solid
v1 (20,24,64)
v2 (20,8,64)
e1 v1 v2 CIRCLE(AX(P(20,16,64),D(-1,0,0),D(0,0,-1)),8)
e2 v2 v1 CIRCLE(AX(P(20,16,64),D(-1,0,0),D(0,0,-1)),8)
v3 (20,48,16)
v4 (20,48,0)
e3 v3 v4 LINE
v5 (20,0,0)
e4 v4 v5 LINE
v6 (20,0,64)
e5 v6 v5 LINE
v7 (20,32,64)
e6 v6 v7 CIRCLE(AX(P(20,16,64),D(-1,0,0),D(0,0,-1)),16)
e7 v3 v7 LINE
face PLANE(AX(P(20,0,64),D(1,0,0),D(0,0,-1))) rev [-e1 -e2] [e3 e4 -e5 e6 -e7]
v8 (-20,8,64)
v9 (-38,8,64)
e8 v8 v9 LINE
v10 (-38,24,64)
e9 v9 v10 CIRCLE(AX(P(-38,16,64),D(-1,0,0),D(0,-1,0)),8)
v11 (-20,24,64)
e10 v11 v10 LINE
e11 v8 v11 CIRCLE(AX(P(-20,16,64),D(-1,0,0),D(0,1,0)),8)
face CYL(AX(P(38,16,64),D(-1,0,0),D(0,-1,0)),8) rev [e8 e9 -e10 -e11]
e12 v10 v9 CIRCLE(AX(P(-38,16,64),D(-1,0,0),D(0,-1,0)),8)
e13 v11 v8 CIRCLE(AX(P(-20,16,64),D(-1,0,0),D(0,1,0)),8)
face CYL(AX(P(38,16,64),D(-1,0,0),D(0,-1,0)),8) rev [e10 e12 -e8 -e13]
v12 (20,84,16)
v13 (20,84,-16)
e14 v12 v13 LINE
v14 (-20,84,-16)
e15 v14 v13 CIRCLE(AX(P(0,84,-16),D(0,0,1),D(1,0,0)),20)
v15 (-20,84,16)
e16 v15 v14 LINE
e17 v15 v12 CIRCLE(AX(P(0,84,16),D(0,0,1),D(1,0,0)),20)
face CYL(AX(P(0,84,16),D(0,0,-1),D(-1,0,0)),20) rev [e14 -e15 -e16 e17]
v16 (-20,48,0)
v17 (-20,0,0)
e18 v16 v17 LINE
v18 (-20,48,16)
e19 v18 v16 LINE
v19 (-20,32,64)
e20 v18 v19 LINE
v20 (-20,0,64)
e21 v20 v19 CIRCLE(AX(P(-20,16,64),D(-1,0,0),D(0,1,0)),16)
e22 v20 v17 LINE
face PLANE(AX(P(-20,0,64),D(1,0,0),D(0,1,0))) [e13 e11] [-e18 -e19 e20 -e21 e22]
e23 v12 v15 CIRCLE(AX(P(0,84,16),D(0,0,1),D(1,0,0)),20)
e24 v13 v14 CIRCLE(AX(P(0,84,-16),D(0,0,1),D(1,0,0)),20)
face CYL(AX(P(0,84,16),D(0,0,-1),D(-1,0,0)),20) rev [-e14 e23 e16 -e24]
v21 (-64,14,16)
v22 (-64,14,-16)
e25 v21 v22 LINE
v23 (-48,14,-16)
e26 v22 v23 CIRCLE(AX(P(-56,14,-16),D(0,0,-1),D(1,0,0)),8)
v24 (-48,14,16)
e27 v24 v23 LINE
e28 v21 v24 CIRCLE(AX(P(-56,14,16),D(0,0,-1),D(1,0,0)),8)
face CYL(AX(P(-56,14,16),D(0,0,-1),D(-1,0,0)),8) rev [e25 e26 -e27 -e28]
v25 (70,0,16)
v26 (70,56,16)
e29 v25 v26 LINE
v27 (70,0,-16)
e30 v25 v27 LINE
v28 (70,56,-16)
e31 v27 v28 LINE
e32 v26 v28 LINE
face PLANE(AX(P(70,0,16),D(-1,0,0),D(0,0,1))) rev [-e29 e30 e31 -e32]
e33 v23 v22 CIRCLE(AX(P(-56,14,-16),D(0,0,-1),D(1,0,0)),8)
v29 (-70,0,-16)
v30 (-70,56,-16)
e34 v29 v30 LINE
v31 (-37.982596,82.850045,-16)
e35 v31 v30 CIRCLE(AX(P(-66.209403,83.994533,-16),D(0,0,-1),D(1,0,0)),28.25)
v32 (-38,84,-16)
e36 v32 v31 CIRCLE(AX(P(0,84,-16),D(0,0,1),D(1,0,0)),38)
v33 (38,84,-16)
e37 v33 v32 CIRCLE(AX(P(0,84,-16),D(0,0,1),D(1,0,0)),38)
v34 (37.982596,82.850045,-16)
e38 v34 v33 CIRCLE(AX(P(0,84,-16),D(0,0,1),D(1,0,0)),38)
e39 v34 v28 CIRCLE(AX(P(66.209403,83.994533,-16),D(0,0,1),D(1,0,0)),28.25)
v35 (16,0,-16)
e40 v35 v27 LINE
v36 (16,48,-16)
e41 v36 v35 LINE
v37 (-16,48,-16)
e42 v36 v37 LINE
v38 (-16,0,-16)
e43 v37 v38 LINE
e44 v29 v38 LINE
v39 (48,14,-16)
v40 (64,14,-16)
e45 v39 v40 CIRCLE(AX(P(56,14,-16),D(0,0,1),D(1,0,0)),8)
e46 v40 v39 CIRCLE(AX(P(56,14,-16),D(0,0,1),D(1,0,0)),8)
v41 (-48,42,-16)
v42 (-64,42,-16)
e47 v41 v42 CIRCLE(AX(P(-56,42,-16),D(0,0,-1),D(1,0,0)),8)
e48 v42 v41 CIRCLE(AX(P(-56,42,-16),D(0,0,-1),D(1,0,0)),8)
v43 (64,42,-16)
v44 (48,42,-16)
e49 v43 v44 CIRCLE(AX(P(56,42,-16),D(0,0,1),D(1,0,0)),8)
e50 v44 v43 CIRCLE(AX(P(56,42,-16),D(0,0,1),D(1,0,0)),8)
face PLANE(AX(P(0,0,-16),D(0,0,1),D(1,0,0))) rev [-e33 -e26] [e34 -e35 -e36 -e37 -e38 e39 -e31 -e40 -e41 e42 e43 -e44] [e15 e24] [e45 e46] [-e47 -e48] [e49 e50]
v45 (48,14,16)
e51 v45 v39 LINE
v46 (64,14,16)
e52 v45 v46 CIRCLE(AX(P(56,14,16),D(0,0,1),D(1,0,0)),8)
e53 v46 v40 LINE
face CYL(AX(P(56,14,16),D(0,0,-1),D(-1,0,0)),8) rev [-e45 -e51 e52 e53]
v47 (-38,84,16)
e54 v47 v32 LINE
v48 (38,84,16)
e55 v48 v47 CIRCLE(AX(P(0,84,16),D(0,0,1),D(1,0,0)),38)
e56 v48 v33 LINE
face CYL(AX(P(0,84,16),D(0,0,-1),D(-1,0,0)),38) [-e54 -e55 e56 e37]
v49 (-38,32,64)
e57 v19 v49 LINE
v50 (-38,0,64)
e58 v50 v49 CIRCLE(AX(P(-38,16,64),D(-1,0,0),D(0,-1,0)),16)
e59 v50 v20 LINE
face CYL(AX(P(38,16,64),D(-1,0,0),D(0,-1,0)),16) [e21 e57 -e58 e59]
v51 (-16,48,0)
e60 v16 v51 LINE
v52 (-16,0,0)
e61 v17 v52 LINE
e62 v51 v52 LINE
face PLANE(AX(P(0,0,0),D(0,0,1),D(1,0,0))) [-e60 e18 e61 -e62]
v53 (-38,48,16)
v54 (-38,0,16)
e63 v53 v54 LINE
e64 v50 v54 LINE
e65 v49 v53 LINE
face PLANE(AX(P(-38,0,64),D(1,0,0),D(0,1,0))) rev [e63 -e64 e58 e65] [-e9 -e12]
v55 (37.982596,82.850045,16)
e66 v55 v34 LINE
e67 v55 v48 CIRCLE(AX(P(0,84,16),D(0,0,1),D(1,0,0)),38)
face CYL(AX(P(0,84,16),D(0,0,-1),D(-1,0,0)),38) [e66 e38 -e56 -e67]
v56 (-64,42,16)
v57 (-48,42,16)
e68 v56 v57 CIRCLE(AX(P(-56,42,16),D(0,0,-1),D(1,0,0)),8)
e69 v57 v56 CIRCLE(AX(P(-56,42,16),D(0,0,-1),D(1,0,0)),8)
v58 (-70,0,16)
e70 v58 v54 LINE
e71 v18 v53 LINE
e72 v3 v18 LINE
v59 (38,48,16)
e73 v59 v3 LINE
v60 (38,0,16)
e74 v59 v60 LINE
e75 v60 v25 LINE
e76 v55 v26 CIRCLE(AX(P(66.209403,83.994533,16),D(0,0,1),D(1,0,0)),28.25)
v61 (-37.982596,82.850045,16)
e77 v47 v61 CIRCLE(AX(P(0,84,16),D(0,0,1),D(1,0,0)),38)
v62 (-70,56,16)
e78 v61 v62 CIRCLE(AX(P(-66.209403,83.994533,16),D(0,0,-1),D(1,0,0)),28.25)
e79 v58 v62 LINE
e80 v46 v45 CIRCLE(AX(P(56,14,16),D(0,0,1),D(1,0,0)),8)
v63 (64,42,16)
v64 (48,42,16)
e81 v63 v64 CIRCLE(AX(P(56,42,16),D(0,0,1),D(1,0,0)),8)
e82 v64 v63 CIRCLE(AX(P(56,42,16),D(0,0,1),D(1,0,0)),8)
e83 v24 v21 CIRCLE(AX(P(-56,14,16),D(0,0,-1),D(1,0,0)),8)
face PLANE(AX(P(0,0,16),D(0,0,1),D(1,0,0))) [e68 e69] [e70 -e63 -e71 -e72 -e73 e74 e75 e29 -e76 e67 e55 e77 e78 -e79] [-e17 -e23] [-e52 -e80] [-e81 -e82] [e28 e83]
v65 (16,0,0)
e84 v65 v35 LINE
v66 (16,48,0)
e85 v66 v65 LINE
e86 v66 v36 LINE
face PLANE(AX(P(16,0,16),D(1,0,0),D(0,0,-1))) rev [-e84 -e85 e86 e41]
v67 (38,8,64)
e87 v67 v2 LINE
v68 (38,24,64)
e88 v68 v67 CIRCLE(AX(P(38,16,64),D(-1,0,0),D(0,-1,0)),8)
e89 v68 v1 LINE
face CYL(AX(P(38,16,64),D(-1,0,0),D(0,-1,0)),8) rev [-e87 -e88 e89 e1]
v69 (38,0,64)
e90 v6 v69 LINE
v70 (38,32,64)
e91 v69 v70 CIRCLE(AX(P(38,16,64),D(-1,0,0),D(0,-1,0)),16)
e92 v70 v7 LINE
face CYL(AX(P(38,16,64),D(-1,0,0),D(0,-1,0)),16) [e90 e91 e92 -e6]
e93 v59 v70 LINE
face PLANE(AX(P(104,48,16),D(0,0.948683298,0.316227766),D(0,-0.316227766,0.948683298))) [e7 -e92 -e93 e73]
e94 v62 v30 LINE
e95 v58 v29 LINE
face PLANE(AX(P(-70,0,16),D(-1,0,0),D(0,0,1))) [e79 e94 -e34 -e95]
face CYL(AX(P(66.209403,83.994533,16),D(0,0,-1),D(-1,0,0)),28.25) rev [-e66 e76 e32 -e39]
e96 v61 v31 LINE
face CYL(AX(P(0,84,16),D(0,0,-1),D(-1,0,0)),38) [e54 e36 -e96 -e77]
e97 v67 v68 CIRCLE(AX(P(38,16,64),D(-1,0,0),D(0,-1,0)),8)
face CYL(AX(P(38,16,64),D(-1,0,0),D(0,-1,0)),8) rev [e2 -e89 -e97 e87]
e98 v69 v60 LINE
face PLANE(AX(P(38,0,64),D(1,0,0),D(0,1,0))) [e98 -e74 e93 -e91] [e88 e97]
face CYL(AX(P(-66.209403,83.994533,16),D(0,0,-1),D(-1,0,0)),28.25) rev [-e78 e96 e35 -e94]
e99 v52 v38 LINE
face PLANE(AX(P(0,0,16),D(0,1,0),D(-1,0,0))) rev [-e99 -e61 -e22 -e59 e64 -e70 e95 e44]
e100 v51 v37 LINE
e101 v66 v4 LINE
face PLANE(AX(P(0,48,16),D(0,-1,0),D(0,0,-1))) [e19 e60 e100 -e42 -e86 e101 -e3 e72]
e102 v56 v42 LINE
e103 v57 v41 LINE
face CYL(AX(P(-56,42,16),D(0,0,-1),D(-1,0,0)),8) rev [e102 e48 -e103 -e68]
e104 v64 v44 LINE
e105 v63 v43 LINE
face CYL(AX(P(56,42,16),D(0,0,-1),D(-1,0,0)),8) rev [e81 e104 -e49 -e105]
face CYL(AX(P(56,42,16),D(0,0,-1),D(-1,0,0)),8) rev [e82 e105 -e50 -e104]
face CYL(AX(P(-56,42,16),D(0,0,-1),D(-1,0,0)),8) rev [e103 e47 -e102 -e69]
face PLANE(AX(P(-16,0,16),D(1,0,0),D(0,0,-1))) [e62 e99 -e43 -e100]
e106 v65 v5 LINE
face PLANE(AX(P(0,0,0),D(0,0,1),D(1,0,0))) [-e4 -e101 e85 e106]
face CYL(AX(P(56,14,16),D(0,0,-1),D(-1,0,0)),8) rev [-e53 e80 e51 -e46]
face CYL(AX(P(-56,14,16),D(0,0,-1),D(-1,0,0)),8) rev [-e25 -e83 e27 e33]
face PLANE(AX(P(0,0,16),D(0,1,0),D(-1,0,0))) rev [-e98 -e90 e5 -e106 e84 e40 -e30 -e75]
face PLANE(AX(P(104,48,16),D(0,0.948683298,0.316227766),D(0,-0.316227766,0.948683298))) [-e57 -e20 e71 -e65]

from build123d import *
from build123d.topology import SkipClean

# Parameters (mm, degrees)
BRACKET_MASTER_PROFILE_SKETCH_R   = 8
BRACKET_MASTER_PROFILE_SKETCH_R_2 = 20
BASE_BLOCK_32MM_DEPTH             = 16
SKETCH1_5_W                       = 18
SKETCH1_5_H                       = 48
BORE_BOSS_BODY_64MM_DEPTH         = 64
CLEVIS_LUGS_76MM_DEPTH            = 76
LUG_PROFILE_CUT_A_DEPTH           = 142
LUG_PROFILE_CUT_B_DEPTH           = 142
SKETCH1_6_W                       = 32
SKETCH1_6_H                       = 48
PROFILE_CUT_131MM_DEPTH           = 131
SKETCH1_7_W                       = 18
SKETCH1_7_H                       = 48
PROFILE_BOSS_16MM_DEPTH           = 16
SKETCH1_15_W                      = 4
SKETCH1_15_H                      = 48
PROFILE_BOSS_32MM_DEPTH           = 16
SKETCH1_16_W                      = 4
SKETCH1_16_H                      = 48
THROUGH_CUT_147MM_DEPTH           = 147


with BuildPart() as part:
    # Bracket Master Profile Sketch → Base Block 32mm (new, symmetric)
    with BuildSketch(Plane.XY):
        with BuildLine():
            Line((-70, 56), (-70, 0))
            Line((-70, 0), (-38, 0))
            Line((-38, 0), (-38, 48))
            Line((-38, 48), (-20, 48))
            Line((-20, 48), (-16, 48))
            Line((-16, 48), (16, 48))
            Line((16, 48), (20, 48))
            Line((20, 48), (38, 48))
            Line((38, 48), (38, 0))
            Line((38, 0), (70, 0))
            Line((70, 0), (70, 56))
            ThreePointArc((70, 56), (48.056901395, 62.34853625), (37.98259606, 82.850044997))
            ThreePointArc((37.98259606, 82.850044997), (0, 122), (-37.98259606, 82.850044997))
            ThreePointArc((-37.98259606, 82.850044997), (-48.056901395, 62.34853625), (-70, 56))
        make_face()
        with Locations((-56, 14)):
            Circle(BRACKET_MASTER_PROFILE_SKETCH_R, mode=Mode.SUBTRACT)
        with Locations((-56, 42)):
            Circle(BRACKET_MASTER_PROFILE_SKETCH_R, mode=Mode.SUBTRACT)
        with Locations((56, 14)):
            Circle(BRACKET_MASTER_PROFILE_SKETCH_R, mode=Mode.SUBTRACT)
        with Locations((56, 42)):
            Circle(BRACKET_MASTER_PROFILE_SKETCH_R, mode=Mode.SUBTRACT)
        with Locations((0, 84)):
            Circle(BRACKET_MASTER_PROFILE_SKETCH_R_2, mode=Mode.SUBTRACT)
    extrude(amount=BASE_BLOCK_32MM_DEPTH, both=True)

    # Sketch1_5 → Bore Boss Body 64mm (add)
    with BuildSketch(Plane.XY):
        with Locations((-29, 24)):
            Rectangle(SKETCH1_5_W, SKETCH1_5_H)
        with Locations((29, 24)):
            Rectangle(SKETCH1_5_W, SKETCH1_5_H)
    extrude(amount=BORE_BOSS_BODY_64MM_DEPTH)

    # Clevis Lug Profile Sketch → Clevis Lugs 76mm (add)
    with BuildSketch(Plane.ZY.offset(38)):
        with BuildLine():
            ThreePointArc((64, 32), (48, 16), (64, 0))
            Line((64, 0), (64, 8))
            ThreePointArc((64, 8), (56, 16), (64, 24))
            Line((64, 24), (64, 32))
        make_face()
        with BuildLine():
            Line((64, 8), (64, 0))
            ThreePointArc((64, 0), (75.313708499, 4.686291501), (80, 16))
            ThreePointArc((80, 16), (75.313708499, 27.313708499), (64, 32))
            Line((64, 32), (64, 24))
            ThreePointArc((64, 24), (69.656854249, 21.656854249), (72, 16))
            ThreePointArc((72, 16), (69.656854249, 10.343145751), (64, 8))
        make_face()
        with BuildLine():
            ThreePointArc((64, 32), (48, 16), (64, 0))
            Line((64, 0), (64, 8))
            ThreePointArc((64, 8), (56, 16), (64, 24))
            Line((64, 24), (64, 32))
        make_face()
        with BuildLine():
            Line((64, 8), (64, 0))
            ThreePointArc((64, 0), (75.313708499, 4.686291501), (80, 16))
            ThreePointArc((80, 16), (75.313708499, 27.313708499), (64, 32))
            Line((64, 32), (64, 24))
            ThreePointArc((64, 24), (69.656854249, 21.656854249), (72, 16))
            ThreePointArc((72, 16), (69.656854249, 10.343145751), (64, 8))
        make_face()
    extrude(amount=-CLEVIS_LUGS_76MM_DEPTH)

    # Sketch2_3 → Lug Profile Cut A (cut)
    with SkipClean():  # the faces are left unmerged after this step: merging them gives an invalid solid
        with BuildSketch(Plane.ZY.offset(38)):
            with BuildLine():
                ThreePointArc((64, 24), (56, 16), (64, 8))
                Line((64, 8), (64, 16))
                Line((64, 16), (64, 24))
            make_face()
            with BuildLine():
                Line((64, 16), (64, 8))
                ThreePointArc((64, 8), (69.656854249, 10.343145751), (72, 16))
                ThreePointArc((72, 16), (69.656854249, 21.656854249), (64, 24))
                Line((64, 24), (64, 16))
            make_face()
        extrude(amount=-LUG_PROFILE_CUT_A_DEPTH, mode=Mode.SUBTRACT)

    # Sketch2_4 → Lug Profile Cut B (cut)
    with SkipClean():  # the faces are left unmerged after this step: merging them gives an invalid solid
        with BuildSketch(Plane.ZY.offset(38)):
            Polygon((16, 48), (64, 32), (64, 48), align=None)
        extrude(amount=-LUG_PROFILE_CUT_B_DEPTH, mode=Mode.SUBTRACT)

    # Sketch1_6 → Profile Cut 131mm (cut)
    with SkipClean():  # the faces are left unmerged after this step: merging them gives an invalid solid
        with BuildSketch(Plane.XY):
            with Locations((0, 24)):
                Rectangle(SKETCH1_6_W, SKETCH1_6_H)
        extrude(amount=PROFILE_CUT_131MM_DEPTH, mode=Mode.SUBTRACT)

    # Sketch1_7 → Profile Boss 16mm (add)
    with SkipClean():  # the faces are left unmerged after this step: merging them gives an invalid solid
        with BuildSketch(Plane.XY):
            with Locations((-29, 24)):
                Rectangle(SKETCH1_7_W, SKETCH1_7_H)
            with Locations((29, 24)):
                Rectangle(SKETCH1_7_W, SKETCH1_7_H)
        extrude(amount=-PROFILE_BOSS_16MM_DEPTH)

    # Sketch1_15 → Profile Boss 32mm (add, symmetric)
    with SkipClean():  # the faces are left unmerged after this step: merging them gives an invalid solid
        with BuildSketch(Plane.XY):
            with Locations((-18, 24)):
                Rectangle(SKETCH1_15_W, SKETCH1_15_H)
            with Locations((18, 24)):
                Rectangle(SKETCH1_15_W, SKETCH1_15_H)
        extrude(amount=PROFILE_BOSS_32MM_DEPTH, both=True)

    # Sketch1_16 → Through Cut 147mm (cut)
    with SkipClean():  # the faces are left unmerged after this step: merging them gives an invalid solid
        with BuildSketch(Plane.XY):
            with Locations((-18, 24)):
                Rectangle(SKETCH1_16_W, SKETCH1_16_H)
            with Locations((18, 24)):
                Rectangle(SKETCH1_16_W, SKETCH1_16_H)
        extrude(amount=THROUGH_CUT_147MM_DEPTH, mode=Mode.SUBTRACT)


solid = part.part
